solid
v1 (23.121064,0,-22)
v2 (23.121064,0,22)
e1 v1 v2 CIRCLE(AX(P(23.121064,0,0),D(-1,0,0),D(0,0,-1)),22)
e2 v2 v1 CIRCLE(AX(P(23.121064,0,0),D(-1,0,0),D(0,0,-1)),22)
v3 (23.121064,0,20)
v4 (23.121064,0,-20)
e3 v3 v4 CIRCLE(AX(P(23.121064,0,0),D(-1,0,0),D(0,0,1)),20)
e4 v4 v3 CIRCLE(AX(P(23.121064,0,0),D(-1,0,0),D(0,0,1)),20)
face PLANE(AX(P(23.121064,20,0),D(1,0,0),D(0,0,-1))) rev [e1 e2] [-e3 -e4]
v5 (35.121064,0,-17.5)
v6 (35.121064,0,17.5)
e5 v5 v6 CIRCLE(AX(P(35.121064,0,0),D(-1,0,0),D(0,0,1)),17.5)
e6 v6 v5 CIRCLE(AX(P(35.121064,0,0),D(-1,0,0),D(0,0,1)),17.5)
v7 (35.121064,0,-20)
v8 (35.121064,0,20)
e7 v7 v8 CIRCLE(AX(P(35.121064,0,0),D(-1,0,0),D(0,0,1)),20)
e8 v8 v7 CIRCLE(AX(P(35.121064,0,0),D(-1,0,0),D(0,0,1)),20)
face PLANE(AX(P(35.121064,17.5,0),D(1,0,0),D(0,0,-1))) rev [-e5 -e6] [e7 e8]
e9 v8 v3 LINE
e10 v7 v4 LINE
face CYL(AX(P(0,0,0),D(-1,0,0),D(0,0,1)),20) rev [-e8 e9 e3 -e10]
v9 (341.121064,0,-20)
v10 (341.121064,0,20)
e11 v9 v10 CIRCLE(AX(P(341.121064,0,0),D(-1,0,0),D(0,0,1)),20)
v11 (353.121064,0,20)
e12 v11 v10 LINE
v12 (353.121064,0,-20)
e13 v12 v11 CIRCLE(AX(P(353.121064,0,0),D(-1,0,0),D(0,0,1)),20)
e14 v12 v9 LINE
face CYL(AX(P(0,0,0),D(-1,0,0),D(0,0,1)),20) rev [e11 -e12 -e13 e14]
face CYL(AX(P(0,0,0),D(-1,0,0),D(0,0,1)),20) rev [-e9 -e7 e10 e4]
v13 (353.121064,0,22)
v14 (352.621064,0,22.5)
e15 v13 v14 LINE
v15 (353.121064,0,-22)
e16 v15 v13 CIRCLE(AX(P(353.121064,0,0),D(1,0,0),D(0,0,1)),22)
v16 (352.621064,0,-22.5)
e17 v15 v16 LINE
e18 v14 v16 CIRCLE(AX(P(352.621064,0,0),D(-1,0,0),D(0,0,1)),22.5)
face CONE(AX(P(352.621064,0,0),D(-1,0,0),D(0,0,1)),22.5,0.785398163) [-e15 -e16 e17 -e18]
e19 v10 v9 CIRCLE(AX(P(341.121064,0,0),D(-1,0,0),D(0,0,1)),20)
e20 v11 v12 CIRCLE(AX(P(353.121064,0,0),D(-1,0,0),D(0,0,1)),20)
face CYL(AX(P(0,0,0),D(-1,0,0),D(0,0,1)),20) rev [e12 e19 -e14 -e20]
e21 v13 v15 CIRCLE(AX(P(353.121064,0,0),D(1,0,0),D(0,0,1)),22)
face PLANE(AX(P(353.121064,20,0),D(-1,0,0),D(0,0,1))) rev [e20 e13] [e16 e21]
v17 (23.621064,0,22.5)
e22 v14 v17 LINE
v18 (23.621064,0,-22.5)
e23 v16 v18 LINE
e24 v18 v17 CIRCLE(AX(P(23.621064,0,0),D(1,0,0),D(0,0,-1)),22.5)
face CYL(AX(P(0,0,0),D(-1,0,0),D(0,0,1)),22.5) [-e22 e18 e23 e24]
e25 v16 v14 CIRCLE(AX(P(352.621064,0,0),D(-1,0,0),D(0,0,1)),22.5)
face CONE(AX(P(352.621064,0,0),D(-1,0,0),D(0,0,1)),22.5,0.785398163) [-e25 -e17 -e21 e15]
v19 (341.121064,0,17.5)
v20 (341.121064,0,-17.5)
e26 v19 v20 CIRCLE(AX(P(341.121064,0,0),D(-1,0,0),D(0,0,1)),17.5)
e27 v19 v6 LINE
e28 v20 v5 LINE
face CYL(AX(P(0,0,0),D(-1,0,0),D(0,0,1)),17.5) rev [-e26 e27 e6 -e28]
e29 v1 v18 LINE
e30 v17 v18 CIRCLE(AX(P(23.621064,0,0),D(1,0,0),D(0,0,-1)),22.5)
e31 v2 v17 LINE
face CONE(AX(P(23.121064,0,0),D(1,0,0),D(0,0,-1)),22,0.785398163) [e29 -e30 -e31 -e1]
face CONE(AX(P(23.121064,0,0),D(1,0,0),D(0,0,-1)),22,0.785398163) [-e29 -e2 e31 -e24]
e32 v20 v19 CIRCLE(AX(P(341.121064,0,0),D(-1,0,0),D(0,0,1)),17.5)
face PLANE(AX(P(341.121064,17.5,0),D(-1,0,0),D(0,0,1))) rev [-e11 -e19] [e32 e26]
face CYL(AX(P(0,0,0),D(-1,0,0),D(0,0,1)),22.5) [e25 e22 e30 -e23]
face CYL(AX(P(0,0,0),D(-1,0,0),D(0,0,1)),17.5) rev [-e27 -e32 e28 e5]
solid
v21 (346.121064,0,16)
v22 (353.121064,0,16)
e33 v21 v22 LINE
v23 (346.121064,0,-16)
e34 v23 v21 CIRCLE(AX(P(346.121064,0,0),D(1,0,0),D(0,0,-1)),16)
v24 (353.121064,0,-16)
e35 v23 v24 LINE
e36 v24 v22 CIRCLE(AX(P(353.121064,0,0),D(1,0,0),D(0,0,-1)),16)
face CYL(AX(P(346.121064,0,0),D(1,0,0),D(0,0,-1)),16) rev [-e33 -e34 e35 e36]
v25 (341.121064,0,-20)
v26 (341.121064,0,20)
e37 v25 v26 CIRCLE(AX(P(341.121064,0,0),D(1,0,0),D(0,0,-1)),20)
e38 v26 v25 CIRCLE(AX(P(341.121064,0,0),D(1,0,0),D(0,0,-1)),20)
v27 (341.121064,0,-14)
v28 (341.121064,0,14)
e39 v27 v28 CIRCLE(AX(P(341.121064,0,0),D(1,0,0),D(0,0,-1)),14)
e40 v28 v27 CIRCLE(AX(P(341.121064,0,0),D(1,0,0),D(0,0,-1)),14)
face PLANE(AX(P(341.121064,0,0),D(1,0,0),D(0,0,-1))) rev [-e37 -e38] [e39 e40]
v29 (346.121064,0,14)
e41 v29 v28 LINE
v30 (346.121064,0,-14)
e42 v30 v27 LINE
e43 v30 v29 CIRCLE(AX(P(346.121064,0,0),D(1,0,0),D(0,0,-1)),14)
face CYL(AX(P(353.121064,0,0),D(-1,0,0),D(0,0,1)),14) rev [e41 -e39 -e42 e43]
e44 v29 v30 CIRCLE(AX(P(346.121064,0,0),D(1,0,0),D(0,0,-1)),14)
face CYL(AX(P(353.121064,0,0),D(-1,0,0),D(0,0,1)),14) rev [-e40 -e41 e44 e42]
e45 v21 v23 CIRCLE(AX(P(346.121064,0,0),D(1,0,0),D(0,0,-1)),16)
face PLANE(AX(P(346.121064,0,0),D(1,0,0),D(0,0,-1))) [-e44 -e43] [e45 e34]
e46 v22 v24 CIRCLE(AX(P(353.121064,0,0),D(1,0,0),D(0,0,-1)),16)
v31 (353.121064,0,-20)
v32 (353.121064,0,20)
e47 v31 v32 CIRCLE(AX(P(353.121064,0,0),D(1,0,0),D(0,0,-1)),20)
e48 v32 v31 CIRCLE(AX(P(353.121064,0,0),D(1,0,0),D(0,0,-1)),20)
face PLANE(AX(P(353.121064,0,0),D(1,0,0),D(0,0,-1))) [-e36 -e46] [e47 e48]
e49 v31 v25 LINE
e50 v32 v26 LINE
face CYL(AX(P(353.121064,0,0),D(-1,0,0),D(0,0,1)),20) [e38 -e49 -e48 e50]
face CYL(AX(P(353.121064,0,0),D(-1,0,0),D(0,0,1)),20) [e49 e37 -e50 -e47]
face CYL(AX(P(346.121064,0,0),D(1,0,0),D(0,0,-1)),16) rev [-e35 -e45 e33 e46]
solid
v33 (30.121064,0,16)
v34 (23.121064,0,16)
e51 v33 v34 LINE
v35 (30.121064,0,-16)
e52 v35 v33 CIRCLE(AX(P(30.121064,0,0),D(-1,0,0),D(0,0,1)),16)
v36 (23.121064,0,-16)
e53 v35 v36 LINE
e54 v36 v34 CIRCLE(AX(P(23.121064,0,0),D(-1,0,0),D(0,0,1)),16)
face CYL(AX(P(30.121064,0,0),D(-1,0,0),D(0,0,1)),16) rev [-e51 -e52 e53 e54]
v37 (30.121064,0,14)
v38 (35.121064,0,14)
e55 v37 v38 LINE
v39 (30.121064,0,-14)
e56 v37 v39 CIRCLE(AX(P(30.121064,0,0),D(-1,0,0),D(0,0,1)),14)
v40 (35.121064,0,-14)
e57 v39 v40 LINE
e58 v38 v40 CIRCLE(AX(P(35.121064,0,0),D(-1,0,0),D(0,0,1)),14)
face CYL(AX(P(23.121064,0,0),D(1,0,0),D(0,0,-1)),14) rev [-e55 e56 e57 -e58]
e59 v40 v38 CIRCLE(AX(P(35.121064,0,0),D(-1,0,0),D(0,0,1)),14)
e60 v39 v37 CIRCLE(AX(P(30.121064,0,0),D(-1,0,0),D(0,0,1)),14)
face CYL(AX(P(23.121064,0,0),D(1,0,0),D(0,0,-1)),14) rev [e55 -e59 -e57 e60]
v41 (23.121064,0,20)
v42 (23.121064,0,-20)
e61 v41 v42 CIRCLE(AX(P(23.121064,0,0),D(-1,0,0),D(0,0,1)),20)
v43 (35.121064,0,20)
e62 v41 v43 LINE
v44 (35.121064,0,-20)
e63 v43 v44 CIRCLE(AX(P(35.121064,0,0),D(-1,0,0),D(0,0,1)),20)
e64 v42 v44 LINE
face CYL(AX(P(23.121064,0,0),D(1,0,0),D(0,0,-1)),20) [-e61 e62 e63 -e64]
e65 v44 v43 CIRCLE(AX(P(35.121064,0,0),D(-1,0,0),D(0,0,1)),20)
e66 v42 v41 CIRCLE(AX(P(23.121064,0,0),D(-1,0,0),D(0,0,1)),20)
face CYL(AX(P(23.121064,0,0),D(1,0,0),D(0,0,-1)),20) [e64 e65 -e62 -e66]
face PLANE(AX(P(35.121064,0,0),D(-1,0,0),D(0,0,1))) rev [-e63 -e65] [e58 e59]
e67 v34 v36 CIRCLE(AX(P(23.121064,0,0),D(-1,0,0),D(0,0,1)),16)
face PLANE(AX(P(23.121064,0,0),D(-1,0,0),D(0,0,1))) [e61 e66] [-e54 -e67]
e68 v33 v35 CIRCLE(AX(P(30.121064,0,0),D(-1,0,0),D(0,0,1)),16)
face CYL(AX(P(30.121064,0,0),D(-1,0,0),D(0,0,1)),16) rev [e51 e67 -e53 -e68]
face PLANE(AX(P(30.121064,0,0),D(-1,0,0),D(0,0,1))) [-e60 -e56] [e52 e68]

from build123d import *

# Parameters (mm, degrees)
CHAMFER1_SIZE       = 0.5
SKETCH2_R           = 20
SKETCH2_R_2         = 14
BOSS_EXTRUDE1_DEPTH = 12
SKETCH4_R           = 16
CUT_EXTRUDE1_DEPTH  = 7
SKETCH5_R           = 20
SKETCH5_R_2         = 14
BOSS_EXTRUDE2_DEPTH = 12
SKETCH7_R           = 16
CUT_EXTRUDE2_DEPTH  = 7


with BuildPart() as part:
    # Sketch1 → Revolve1 (revolve)
    with BuildSketch(Plane.XY, mode=Mode.PRIVATE) as revolve1_sk:
        Polygon((35.121064285, 17.5), (341.121064285, 17.5), (341.121064285, 20), (353.121064285, 20), (353.121064285, 22.5), (23.121064285, 22.5), (23.121064285, 20), (35.121064285, 20), align=None)
    revolve(revolve1_sk.sketch.rotate(Axis((0, 0, 0), (1, 0, 0)), 90), axis=Axis((0, 0, 0), (1, 0, 0)))

    # Chamfer1
    chamfer1_edges = [part.edges().sort_by_distance(p)[0] for p in [
        (353.121064285, 0, -22.5),
        (23.121064285, 0, -22.5),
    ]]
    chamfer(chamfer1_edges, length=CHAMFER1_SIZE)


with BuildPart() as body_2:
    # Sketch2 → Boss-Extrude1 (new body)
    with BuildSketch(Plane(origin=(341.121064285, 0, 0), x_dir=(0, 0, -1), z_dir=(1, 0, 0))):
        Circle(SKETCH2_R)
        Circle(SKETCH2_R_2, mode=Mode.SUBTRACT)
    extrude(amount=BOSS_EXTRUDE1_DEPTH)

    # Sketch4 → Cut-Extrude1 (cut)
    with BuildSketch(Plane(origin=(353.121064285, 0, 0), x_dir=(0, 0, -1), z_dir=(1, 0, 0))):
        Circle(SKETCH4_R)
    extrude(amount=-CUT_EXTRUDE1_DEPTH, mode=Mode.SUBTRACT)


with BuildPart() as body_3:
    # Sketch5 → Boss-Extrude2 (new body)
    with BuildSketch(Plane.ZY.offset(-35.121064285)):
        Circle(SKETCH5_R)
        Circle(SKETCH5_R_2, mode=Mode.SUBTRACT)
    extrude(amount=BOSS_EXTRUDE2_DEPTH)

    # Sketch7 → Cut-Extrude2 (cut)
    with BuildSketch(Plane.ZY.offset(-23.121064285)):
        Circle(SKETCH7_R)
    extrude(amount=-CUT_EXTRUDE2_DEPTH, mode=Mode.SUBTRACT)


solid = Compound([part.part, body_2.part, body_3.part])
